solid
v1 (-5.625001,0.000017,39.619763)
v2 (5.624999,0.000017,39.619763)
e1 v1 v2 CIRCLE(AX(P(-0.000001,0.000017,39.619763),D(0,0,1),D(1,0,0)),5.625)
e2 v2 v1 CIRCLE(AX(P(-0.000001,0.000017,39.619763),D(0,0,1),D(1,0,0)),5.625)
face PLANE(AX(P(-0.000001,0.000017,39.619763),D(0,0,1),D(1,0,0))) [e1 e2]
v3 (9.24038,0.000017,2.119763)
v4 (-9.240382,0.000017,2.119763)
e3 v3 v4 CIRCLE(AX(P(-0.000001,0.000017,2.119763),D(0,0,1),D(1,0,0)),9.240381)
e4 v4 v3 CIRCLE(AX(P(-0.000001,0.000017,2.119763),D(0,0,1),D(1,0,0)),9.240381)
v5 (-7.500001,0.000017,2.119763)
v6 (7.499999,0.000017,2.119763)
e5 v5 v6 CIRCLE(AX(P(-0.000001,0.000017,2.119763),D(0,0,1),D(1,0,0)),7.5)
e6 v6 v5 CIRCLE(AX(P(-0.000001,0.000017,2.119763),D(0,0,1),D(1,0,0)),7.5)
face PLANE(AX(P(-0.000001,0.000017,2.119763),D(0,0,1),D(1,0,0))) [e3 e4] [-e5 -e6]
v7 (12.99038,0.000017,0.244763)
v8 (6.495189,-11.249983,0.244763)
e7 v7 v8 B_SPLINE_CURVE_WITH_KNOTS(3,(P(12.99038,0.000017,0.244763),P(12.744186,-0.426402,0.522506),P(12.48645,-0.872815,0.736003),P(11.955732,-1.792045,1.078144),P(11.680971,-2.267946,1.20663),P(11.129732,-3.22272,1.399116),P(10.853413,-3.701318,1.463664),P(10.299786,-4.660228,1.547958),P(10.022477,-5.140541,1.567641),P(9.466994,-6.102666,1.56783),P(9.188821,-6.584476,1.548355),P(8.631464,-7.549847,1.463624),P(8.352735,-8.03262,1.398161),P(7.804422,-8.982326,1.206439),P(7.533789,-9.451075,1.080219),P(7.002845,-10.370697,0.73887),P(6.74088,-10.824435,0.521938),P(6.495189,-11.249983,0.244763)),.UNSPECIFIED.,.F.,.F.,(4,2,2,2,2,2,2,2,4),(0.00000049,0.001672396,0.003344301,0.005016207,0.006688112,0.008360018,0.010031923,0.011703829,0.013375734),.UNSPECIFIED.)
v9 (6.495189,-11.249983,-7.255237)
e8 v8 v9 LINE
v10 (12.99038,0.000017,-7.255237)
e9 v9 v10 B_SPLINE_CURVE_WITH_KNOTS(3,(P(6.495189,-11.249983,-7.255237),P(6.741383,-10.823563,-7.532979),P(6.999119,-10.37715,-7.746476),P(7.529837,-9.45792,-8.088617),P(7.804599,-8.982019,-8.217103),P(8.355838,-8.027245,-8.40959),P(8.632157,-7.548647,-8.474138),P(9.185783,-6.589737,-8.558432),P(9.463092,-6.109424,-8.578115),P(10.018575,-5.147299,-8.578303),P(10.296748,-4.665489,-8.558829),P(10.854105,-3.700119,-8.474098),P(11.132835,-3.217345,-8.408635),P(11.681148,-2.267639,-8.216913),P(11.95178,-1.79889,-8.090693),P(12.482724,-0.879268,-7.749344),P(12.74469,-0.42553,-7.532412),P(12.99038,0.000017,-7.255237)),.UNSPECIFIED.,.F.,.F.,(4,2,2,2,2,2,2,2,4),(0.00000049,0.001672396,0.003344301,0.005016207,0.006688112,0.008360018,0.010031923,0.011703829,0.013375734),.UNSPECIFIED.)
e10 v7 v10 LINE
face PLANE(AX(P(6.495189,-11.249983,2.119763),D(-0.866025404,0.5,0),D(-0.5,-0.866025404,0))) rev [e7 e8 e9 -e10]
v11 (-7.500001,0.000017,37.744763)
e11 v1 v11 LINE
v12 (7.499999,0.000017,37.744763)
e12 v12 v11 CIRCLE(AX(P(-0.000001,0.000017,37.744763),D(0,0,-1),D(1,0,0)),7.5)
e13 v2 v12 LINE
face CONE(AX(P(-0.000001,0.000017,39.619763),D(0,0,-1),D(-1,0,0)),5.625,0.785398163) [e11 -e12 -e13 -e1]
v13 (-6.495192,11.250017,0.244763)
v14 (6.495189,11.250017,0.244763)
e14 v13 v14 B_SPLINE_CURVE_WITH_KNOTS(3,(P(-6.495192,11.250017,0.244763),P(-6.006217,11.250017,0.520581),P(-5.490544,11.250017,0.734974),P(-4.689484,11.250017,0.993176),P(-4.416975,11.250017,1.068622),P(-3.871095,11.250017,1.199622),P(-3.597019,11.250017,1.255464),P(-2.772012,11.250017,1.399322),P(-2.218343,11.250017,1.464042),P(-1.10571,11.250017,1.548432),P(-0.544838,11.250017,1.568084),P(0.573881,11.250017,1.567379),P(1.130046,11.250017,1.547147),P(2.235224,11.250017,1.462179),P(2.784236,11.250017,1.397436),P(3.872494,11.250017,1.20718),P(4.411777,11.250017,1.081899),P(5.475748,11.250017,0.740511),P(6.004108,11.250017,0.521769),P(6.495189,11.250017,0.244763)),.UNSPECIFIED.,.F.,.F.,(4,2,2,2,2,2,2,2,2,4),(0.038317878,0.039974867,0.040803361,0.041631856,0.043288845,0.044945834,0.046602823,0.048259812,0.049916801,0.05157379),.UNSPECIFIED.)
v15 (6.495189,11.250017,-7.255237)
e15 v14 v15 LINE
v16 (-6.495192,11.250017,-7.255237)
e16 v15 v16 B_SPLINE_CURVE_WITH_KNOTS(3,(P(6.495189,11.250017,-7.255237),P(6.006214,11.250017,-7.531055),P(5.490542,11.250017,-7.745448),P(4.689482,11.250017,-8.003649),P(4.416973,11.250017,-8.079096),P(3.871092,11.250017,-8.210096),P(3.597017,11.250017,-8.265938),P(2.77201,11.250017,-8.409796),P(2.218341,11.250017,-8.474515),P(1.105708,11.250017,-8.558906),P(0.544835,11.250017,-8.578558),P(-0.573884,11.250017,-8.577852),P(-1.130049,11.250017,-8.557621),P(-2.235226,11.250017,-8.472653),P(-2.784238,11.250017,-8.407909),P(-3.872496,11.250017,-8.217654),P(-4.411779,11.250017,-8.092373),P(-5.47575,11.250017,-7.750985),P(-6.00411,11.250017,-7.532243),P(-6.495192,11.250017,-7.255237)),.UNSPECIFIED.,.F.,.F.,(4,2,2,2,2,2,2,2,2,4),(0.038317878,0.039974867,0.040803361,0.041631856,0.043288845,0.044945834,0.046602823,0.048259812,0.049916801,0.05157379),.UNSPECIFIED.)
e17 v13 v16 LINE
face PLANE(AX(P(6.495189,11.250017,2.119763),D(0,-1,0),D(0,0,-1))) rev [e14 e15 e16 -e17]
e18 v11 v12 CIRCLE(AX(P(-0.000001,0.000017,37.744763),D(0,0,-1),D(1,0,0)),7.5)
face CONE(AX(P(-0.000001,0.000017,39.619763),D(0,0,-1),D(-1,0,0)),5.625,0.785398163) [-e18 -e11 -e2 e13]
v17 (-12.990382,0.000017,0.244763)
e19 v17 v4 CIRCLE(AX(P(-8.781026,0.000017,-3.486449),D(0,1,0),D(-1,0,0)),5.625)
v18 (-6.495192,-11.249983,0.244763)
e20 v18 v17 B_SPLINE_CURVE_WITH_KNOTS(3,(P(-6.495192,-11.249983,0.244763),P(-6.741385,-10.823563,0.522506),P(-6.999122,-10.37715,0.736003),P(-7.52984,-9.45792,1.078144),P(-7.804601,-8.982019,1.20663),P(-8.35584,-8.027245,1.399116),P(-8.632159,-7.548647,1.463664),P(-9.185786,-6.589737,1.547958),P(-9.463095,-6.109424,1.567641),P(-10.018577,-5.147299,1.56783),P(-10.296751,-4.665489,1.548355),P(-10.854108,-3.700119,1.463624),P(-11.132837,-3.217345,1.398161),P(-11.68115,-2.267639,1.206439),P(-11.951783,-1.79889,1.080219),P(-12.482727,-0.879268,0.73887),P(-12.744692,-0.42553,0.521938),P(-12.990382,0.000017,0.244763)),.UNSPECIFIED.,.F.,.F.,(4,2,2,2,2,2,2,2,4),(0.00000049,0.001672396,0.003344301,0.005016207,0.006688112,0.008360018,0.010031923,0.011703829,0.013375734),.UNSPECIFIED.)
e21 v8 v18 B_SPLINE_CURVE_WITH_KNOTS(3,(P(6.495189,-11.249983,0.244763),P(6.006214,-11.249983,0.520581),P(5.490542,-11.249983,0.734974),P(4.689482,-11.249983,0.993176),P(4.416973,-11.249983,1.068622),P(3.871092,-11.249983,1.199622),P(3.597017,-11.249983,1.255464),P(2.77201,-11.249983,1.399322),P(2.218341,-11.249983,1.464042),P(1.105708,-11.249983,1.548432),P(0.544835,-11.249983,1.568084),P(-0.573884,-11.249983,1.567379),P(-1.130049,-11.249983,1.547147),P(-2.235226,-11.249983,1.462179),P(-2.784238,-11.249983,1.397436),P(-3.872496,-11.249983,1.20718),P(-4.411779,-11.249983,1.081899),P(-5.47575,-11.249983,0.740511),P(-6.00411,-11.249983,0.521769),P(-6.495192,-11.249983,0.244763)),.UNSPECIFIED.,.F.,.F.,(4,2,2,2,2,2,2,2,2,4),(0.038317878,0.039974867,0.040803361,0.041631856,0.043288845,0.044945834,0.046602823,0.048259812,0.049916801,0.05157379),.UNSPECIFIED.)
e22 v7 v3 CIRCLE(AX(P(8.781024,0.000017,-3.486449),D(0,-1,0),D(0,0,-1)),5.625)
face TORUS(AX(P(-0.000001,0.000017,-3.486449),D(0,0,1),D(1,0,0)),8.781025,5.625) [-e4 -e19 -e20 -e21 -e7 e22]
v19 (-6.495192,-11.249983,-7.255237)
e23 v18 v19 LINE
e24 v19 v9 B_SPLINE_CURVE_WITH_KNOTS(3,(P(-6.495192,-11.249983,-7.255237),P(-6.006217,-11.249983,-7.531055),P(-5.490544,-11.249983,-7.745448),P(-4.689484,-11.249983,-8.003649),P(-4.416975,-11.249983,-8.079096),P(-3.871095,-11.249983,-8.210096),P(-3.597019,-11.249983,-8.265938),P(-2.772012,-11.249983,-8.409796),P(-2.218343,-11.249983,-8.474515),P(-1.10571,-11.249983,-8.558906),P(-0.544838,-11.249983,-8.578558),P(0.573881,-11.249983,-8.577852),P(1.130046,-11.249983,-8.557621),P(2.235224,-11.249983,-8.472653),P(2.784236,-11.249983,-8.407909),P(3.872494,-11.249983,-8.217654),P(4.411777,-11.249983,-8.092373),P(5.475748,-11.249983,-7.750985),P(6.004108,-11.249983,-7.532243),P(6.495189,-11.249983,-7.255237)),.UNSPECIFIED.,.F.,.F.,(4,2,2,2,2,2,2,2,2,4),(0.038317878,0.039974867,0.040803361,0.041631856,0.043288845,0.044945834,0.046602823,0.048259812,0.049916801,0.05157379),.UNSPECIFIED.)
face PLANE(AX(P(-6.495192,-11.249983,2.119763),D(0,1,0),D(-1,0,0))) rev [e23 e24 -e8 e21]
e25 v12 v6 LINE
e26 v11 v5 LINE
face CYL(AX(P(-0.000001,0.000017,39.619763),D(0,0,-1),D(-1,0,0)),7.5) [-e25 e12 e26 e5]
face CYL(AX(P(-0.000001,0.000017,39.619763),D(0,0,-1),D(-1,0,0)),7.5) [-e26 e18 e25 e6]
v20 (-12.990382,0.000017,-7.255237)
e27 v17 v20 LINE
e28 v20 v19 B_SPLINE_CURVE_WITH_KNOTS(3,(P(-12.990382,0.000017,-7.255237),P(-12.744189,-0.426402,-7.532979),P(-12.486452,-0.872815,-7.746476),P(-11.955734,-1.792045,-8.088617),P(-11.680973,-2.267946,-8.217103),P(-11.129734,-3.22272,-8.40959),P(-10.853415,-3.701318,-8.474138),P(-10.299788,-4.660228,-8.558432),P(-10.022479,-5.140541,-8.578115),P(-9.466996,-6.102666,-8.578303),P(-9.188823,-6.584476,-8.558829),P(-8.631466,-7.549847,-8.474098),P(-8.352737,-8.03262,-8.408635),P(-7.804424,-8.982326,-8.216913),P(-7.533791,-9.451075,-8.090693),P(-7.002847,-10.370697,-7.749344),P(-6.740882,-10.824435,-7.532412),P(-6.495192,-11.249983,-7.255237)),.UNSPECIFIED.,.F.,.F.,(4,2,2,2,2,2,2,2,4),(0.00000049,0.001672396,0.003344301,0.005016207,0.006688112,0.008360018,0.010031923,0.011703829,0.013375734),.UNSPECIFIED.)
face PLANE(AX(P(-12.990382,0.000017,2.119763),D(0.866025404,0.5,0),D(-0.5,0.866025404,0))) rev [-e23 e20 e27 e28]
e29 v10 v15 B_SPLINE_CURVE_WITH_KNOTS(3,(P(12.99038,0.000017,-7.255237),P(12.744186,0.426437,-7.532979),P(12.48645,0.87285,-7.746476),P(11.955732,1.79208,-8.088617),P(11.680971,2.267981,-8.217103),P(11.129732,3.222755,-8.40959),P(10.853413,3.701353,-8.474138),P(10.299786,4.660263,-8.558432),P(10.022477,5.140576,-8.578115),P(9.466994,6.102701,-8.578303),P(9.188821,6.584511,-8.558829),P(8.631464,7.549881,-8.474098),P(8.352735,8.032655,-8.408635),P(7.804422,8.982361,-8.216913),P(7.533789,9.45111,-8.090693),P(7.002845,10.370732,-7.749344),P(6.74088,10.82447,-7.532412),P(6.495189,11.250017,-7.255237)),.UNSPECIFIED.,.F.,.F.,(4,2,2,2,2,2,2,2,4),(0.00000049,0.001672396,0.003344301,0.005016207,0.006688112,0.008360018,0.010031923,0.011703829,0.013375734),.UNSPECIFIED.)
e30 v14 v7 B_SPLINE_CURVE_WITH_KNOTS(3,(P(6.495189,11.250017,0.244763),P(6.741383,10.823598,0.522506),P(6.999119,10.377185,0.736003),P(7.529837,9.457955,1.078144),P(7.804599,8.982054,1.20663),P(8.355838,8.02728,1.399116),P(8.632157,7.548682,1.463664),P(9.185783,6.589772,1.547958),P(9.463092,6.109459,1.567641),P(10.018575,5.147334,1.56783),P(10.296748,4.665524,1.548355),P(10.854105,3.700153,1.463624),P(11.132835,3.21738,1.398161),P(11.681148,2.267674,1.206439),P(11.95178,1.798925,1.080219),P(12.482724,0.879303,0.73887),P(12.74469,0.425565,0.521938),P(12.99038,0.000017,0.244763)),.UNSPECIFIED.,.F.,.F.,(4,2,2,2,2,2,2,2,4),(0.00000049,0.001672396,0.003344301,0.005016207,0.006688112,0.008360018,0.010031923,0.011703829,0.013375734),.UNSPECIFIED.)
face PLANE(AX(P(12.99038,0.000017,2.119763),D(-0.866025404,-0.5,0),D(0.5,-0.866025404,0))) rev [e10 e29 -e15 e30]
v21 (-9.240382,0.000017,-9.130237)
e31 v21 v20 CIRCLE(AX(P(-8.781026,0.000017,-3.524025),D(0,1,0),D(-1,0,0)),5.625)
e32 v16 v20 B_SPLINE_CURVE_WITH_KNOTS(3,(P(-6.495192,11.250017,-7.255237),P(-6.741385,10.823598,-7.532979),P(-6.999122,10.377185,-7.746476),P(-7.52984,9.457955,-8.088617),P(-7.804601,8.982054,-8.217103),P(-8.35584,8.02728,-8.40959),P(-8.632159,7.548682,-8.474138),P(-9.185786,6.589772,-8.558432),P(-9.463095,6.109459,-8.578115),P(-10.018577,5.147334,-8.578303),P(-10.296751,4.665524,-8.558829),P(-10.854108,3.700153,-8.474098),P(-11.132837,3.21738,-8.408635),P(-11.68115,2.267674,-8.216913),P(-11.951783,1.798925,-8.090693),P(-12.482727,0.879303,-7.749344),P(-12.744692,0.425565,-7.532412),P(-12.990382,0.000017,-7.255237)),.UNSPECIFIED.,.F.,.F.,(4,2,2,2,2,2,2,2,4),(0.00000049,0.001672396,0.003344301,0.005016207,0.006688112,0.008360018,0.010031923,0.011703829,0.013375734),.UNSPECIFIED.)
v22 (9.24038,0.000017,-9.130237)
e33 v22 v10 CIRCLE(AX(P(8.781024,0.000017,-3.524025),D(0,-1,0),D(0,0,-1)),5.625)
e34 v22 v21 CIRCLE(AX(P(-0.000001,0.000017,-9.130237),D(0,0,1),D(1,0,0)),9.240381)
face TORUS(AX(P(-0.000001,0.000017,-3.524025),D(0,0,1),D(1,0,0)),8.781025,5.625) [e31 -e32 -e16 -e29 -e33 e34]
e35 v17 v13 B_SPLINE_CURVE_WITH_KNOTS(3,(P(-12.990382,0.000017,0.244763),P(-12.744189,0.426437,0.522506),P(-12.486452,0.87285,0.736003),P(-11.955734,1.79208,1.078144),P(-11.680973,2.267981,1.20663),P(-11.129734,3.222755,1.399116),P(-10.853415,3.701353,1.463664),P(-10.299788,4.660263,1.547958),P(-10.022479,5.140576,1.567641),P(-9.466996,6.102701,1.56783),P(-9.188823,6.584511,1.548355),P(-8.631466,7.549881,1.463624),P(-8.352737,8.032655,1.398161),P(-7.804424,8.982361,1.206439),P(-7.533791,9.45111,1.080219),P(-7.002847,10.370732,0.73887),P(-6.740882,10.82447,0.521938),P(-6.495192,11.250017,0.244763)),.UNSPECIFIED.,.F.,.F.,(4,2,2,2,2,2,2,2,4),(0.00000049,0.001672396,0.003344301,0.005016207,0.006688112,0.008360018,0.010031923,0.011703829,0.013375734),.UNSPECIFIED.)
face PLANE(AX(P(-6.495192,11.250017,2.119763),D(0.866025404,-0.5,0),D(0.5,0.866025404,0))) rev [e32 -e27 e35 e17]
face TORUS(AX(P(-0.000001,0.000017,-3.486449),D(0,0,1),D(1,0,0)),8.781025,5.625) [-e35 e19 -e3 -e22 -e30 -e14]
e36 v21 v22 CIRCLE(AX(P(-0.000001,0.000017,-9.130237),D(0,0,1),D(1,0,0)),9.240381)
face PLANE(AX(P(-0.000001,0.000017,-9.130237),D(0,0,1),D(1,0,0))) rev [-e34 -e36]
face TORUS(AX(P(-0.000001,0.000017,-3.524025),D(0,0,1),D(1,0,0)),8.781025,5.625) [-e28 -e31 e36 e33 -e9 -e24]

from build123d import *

# Parameters (mm, degrees)
BOSS_EXTRUDE1_DEPTH = 6
SKETCH2_R           = 4
BOSS_EXTRUDE2_DEPTH = 20
CHAMFER1_SIZE       = 1
SCALE_1_SCALE       = 1.875


with BuildPart() as part:
    # Sketch1 → Boss-Extrude1 (new body)
    with BuildSketch(Plane.XY):
        Polygon((6.92820323, 0), (3.464101615, 6), (-3.464101615, 6), (-6.92820323, 0), (-3.464101615, -6), (3.464101615, -6), align=None)
    extrude(amount=BOSS_EXTRUDE1_DEPTH)

    # Sketch2 → Boss-Extrude2 (add)
    with BuildSketch(Plane.XY.offset(6)):
        Circle(SKETCH2_R)
    extrude(amount=BOSS_EXTRUDE2_DEPTH)

    # Chamfer1
    chamfer1_edges = [part.edges().sort_by_distance(p)[0] for p in [
        (-4, 0, 26),
    ]]
    chamfer(chamfer1_edges, length=CHAMFER1_SIZE)

    # Sketch3 → Cut-Revolve1 (revolve, cut)
    with BuildSketch(Plane(origin=(0, 0, 0), x_dir=(1, 0, 0), z_dir=(0, 1, 0)), mode=Mode.PRIVATE) as cut_revolve1_sk:
        with BuildLine():
            ThreePointArc((-6.92820323, -1), (-6.024854057, -0.306698347), (-4.92820323, 0))
            Line((-4.92820323, 0), (-8.853828921, 0.851275599))
            Line((-8.853828921, 0.851275599), (-9.311272628, -1))
            Line((-9.311272628, -1), (-6.92820323, -1))
        make_face()
        with BuildLine():
            ThreePointArc((-6.92820323, -5), (-6.024854057, -5.693301653), (-4.92820323, -6))
            Line((-4.92820323, -6), (-8.016018434, -6.744872817))
            Line((-8.016018434, -6.744872817), (-9.311272628, -5))
            Line((-9.311272628, -5), (-6.92820323, -5))
        make_face()
    revolve(cut_revolve1_sk.sketch.rotate(Axis((0, 0, 0), (0, 0, -1)), 180), axis=Axis((0, 0, 0), (0, 0, -1)), mode=Mode.SUBTRACT)


with BuildPart() as part_1:
    # Scale 1: scaled about (1e-08, -1e-08, 10.434688187)
    add(part.part.scale(SCALE_1_SCALE).moved(Location((-9e-09, 9e-09, -9.130352164))))


solid = part_1.part
